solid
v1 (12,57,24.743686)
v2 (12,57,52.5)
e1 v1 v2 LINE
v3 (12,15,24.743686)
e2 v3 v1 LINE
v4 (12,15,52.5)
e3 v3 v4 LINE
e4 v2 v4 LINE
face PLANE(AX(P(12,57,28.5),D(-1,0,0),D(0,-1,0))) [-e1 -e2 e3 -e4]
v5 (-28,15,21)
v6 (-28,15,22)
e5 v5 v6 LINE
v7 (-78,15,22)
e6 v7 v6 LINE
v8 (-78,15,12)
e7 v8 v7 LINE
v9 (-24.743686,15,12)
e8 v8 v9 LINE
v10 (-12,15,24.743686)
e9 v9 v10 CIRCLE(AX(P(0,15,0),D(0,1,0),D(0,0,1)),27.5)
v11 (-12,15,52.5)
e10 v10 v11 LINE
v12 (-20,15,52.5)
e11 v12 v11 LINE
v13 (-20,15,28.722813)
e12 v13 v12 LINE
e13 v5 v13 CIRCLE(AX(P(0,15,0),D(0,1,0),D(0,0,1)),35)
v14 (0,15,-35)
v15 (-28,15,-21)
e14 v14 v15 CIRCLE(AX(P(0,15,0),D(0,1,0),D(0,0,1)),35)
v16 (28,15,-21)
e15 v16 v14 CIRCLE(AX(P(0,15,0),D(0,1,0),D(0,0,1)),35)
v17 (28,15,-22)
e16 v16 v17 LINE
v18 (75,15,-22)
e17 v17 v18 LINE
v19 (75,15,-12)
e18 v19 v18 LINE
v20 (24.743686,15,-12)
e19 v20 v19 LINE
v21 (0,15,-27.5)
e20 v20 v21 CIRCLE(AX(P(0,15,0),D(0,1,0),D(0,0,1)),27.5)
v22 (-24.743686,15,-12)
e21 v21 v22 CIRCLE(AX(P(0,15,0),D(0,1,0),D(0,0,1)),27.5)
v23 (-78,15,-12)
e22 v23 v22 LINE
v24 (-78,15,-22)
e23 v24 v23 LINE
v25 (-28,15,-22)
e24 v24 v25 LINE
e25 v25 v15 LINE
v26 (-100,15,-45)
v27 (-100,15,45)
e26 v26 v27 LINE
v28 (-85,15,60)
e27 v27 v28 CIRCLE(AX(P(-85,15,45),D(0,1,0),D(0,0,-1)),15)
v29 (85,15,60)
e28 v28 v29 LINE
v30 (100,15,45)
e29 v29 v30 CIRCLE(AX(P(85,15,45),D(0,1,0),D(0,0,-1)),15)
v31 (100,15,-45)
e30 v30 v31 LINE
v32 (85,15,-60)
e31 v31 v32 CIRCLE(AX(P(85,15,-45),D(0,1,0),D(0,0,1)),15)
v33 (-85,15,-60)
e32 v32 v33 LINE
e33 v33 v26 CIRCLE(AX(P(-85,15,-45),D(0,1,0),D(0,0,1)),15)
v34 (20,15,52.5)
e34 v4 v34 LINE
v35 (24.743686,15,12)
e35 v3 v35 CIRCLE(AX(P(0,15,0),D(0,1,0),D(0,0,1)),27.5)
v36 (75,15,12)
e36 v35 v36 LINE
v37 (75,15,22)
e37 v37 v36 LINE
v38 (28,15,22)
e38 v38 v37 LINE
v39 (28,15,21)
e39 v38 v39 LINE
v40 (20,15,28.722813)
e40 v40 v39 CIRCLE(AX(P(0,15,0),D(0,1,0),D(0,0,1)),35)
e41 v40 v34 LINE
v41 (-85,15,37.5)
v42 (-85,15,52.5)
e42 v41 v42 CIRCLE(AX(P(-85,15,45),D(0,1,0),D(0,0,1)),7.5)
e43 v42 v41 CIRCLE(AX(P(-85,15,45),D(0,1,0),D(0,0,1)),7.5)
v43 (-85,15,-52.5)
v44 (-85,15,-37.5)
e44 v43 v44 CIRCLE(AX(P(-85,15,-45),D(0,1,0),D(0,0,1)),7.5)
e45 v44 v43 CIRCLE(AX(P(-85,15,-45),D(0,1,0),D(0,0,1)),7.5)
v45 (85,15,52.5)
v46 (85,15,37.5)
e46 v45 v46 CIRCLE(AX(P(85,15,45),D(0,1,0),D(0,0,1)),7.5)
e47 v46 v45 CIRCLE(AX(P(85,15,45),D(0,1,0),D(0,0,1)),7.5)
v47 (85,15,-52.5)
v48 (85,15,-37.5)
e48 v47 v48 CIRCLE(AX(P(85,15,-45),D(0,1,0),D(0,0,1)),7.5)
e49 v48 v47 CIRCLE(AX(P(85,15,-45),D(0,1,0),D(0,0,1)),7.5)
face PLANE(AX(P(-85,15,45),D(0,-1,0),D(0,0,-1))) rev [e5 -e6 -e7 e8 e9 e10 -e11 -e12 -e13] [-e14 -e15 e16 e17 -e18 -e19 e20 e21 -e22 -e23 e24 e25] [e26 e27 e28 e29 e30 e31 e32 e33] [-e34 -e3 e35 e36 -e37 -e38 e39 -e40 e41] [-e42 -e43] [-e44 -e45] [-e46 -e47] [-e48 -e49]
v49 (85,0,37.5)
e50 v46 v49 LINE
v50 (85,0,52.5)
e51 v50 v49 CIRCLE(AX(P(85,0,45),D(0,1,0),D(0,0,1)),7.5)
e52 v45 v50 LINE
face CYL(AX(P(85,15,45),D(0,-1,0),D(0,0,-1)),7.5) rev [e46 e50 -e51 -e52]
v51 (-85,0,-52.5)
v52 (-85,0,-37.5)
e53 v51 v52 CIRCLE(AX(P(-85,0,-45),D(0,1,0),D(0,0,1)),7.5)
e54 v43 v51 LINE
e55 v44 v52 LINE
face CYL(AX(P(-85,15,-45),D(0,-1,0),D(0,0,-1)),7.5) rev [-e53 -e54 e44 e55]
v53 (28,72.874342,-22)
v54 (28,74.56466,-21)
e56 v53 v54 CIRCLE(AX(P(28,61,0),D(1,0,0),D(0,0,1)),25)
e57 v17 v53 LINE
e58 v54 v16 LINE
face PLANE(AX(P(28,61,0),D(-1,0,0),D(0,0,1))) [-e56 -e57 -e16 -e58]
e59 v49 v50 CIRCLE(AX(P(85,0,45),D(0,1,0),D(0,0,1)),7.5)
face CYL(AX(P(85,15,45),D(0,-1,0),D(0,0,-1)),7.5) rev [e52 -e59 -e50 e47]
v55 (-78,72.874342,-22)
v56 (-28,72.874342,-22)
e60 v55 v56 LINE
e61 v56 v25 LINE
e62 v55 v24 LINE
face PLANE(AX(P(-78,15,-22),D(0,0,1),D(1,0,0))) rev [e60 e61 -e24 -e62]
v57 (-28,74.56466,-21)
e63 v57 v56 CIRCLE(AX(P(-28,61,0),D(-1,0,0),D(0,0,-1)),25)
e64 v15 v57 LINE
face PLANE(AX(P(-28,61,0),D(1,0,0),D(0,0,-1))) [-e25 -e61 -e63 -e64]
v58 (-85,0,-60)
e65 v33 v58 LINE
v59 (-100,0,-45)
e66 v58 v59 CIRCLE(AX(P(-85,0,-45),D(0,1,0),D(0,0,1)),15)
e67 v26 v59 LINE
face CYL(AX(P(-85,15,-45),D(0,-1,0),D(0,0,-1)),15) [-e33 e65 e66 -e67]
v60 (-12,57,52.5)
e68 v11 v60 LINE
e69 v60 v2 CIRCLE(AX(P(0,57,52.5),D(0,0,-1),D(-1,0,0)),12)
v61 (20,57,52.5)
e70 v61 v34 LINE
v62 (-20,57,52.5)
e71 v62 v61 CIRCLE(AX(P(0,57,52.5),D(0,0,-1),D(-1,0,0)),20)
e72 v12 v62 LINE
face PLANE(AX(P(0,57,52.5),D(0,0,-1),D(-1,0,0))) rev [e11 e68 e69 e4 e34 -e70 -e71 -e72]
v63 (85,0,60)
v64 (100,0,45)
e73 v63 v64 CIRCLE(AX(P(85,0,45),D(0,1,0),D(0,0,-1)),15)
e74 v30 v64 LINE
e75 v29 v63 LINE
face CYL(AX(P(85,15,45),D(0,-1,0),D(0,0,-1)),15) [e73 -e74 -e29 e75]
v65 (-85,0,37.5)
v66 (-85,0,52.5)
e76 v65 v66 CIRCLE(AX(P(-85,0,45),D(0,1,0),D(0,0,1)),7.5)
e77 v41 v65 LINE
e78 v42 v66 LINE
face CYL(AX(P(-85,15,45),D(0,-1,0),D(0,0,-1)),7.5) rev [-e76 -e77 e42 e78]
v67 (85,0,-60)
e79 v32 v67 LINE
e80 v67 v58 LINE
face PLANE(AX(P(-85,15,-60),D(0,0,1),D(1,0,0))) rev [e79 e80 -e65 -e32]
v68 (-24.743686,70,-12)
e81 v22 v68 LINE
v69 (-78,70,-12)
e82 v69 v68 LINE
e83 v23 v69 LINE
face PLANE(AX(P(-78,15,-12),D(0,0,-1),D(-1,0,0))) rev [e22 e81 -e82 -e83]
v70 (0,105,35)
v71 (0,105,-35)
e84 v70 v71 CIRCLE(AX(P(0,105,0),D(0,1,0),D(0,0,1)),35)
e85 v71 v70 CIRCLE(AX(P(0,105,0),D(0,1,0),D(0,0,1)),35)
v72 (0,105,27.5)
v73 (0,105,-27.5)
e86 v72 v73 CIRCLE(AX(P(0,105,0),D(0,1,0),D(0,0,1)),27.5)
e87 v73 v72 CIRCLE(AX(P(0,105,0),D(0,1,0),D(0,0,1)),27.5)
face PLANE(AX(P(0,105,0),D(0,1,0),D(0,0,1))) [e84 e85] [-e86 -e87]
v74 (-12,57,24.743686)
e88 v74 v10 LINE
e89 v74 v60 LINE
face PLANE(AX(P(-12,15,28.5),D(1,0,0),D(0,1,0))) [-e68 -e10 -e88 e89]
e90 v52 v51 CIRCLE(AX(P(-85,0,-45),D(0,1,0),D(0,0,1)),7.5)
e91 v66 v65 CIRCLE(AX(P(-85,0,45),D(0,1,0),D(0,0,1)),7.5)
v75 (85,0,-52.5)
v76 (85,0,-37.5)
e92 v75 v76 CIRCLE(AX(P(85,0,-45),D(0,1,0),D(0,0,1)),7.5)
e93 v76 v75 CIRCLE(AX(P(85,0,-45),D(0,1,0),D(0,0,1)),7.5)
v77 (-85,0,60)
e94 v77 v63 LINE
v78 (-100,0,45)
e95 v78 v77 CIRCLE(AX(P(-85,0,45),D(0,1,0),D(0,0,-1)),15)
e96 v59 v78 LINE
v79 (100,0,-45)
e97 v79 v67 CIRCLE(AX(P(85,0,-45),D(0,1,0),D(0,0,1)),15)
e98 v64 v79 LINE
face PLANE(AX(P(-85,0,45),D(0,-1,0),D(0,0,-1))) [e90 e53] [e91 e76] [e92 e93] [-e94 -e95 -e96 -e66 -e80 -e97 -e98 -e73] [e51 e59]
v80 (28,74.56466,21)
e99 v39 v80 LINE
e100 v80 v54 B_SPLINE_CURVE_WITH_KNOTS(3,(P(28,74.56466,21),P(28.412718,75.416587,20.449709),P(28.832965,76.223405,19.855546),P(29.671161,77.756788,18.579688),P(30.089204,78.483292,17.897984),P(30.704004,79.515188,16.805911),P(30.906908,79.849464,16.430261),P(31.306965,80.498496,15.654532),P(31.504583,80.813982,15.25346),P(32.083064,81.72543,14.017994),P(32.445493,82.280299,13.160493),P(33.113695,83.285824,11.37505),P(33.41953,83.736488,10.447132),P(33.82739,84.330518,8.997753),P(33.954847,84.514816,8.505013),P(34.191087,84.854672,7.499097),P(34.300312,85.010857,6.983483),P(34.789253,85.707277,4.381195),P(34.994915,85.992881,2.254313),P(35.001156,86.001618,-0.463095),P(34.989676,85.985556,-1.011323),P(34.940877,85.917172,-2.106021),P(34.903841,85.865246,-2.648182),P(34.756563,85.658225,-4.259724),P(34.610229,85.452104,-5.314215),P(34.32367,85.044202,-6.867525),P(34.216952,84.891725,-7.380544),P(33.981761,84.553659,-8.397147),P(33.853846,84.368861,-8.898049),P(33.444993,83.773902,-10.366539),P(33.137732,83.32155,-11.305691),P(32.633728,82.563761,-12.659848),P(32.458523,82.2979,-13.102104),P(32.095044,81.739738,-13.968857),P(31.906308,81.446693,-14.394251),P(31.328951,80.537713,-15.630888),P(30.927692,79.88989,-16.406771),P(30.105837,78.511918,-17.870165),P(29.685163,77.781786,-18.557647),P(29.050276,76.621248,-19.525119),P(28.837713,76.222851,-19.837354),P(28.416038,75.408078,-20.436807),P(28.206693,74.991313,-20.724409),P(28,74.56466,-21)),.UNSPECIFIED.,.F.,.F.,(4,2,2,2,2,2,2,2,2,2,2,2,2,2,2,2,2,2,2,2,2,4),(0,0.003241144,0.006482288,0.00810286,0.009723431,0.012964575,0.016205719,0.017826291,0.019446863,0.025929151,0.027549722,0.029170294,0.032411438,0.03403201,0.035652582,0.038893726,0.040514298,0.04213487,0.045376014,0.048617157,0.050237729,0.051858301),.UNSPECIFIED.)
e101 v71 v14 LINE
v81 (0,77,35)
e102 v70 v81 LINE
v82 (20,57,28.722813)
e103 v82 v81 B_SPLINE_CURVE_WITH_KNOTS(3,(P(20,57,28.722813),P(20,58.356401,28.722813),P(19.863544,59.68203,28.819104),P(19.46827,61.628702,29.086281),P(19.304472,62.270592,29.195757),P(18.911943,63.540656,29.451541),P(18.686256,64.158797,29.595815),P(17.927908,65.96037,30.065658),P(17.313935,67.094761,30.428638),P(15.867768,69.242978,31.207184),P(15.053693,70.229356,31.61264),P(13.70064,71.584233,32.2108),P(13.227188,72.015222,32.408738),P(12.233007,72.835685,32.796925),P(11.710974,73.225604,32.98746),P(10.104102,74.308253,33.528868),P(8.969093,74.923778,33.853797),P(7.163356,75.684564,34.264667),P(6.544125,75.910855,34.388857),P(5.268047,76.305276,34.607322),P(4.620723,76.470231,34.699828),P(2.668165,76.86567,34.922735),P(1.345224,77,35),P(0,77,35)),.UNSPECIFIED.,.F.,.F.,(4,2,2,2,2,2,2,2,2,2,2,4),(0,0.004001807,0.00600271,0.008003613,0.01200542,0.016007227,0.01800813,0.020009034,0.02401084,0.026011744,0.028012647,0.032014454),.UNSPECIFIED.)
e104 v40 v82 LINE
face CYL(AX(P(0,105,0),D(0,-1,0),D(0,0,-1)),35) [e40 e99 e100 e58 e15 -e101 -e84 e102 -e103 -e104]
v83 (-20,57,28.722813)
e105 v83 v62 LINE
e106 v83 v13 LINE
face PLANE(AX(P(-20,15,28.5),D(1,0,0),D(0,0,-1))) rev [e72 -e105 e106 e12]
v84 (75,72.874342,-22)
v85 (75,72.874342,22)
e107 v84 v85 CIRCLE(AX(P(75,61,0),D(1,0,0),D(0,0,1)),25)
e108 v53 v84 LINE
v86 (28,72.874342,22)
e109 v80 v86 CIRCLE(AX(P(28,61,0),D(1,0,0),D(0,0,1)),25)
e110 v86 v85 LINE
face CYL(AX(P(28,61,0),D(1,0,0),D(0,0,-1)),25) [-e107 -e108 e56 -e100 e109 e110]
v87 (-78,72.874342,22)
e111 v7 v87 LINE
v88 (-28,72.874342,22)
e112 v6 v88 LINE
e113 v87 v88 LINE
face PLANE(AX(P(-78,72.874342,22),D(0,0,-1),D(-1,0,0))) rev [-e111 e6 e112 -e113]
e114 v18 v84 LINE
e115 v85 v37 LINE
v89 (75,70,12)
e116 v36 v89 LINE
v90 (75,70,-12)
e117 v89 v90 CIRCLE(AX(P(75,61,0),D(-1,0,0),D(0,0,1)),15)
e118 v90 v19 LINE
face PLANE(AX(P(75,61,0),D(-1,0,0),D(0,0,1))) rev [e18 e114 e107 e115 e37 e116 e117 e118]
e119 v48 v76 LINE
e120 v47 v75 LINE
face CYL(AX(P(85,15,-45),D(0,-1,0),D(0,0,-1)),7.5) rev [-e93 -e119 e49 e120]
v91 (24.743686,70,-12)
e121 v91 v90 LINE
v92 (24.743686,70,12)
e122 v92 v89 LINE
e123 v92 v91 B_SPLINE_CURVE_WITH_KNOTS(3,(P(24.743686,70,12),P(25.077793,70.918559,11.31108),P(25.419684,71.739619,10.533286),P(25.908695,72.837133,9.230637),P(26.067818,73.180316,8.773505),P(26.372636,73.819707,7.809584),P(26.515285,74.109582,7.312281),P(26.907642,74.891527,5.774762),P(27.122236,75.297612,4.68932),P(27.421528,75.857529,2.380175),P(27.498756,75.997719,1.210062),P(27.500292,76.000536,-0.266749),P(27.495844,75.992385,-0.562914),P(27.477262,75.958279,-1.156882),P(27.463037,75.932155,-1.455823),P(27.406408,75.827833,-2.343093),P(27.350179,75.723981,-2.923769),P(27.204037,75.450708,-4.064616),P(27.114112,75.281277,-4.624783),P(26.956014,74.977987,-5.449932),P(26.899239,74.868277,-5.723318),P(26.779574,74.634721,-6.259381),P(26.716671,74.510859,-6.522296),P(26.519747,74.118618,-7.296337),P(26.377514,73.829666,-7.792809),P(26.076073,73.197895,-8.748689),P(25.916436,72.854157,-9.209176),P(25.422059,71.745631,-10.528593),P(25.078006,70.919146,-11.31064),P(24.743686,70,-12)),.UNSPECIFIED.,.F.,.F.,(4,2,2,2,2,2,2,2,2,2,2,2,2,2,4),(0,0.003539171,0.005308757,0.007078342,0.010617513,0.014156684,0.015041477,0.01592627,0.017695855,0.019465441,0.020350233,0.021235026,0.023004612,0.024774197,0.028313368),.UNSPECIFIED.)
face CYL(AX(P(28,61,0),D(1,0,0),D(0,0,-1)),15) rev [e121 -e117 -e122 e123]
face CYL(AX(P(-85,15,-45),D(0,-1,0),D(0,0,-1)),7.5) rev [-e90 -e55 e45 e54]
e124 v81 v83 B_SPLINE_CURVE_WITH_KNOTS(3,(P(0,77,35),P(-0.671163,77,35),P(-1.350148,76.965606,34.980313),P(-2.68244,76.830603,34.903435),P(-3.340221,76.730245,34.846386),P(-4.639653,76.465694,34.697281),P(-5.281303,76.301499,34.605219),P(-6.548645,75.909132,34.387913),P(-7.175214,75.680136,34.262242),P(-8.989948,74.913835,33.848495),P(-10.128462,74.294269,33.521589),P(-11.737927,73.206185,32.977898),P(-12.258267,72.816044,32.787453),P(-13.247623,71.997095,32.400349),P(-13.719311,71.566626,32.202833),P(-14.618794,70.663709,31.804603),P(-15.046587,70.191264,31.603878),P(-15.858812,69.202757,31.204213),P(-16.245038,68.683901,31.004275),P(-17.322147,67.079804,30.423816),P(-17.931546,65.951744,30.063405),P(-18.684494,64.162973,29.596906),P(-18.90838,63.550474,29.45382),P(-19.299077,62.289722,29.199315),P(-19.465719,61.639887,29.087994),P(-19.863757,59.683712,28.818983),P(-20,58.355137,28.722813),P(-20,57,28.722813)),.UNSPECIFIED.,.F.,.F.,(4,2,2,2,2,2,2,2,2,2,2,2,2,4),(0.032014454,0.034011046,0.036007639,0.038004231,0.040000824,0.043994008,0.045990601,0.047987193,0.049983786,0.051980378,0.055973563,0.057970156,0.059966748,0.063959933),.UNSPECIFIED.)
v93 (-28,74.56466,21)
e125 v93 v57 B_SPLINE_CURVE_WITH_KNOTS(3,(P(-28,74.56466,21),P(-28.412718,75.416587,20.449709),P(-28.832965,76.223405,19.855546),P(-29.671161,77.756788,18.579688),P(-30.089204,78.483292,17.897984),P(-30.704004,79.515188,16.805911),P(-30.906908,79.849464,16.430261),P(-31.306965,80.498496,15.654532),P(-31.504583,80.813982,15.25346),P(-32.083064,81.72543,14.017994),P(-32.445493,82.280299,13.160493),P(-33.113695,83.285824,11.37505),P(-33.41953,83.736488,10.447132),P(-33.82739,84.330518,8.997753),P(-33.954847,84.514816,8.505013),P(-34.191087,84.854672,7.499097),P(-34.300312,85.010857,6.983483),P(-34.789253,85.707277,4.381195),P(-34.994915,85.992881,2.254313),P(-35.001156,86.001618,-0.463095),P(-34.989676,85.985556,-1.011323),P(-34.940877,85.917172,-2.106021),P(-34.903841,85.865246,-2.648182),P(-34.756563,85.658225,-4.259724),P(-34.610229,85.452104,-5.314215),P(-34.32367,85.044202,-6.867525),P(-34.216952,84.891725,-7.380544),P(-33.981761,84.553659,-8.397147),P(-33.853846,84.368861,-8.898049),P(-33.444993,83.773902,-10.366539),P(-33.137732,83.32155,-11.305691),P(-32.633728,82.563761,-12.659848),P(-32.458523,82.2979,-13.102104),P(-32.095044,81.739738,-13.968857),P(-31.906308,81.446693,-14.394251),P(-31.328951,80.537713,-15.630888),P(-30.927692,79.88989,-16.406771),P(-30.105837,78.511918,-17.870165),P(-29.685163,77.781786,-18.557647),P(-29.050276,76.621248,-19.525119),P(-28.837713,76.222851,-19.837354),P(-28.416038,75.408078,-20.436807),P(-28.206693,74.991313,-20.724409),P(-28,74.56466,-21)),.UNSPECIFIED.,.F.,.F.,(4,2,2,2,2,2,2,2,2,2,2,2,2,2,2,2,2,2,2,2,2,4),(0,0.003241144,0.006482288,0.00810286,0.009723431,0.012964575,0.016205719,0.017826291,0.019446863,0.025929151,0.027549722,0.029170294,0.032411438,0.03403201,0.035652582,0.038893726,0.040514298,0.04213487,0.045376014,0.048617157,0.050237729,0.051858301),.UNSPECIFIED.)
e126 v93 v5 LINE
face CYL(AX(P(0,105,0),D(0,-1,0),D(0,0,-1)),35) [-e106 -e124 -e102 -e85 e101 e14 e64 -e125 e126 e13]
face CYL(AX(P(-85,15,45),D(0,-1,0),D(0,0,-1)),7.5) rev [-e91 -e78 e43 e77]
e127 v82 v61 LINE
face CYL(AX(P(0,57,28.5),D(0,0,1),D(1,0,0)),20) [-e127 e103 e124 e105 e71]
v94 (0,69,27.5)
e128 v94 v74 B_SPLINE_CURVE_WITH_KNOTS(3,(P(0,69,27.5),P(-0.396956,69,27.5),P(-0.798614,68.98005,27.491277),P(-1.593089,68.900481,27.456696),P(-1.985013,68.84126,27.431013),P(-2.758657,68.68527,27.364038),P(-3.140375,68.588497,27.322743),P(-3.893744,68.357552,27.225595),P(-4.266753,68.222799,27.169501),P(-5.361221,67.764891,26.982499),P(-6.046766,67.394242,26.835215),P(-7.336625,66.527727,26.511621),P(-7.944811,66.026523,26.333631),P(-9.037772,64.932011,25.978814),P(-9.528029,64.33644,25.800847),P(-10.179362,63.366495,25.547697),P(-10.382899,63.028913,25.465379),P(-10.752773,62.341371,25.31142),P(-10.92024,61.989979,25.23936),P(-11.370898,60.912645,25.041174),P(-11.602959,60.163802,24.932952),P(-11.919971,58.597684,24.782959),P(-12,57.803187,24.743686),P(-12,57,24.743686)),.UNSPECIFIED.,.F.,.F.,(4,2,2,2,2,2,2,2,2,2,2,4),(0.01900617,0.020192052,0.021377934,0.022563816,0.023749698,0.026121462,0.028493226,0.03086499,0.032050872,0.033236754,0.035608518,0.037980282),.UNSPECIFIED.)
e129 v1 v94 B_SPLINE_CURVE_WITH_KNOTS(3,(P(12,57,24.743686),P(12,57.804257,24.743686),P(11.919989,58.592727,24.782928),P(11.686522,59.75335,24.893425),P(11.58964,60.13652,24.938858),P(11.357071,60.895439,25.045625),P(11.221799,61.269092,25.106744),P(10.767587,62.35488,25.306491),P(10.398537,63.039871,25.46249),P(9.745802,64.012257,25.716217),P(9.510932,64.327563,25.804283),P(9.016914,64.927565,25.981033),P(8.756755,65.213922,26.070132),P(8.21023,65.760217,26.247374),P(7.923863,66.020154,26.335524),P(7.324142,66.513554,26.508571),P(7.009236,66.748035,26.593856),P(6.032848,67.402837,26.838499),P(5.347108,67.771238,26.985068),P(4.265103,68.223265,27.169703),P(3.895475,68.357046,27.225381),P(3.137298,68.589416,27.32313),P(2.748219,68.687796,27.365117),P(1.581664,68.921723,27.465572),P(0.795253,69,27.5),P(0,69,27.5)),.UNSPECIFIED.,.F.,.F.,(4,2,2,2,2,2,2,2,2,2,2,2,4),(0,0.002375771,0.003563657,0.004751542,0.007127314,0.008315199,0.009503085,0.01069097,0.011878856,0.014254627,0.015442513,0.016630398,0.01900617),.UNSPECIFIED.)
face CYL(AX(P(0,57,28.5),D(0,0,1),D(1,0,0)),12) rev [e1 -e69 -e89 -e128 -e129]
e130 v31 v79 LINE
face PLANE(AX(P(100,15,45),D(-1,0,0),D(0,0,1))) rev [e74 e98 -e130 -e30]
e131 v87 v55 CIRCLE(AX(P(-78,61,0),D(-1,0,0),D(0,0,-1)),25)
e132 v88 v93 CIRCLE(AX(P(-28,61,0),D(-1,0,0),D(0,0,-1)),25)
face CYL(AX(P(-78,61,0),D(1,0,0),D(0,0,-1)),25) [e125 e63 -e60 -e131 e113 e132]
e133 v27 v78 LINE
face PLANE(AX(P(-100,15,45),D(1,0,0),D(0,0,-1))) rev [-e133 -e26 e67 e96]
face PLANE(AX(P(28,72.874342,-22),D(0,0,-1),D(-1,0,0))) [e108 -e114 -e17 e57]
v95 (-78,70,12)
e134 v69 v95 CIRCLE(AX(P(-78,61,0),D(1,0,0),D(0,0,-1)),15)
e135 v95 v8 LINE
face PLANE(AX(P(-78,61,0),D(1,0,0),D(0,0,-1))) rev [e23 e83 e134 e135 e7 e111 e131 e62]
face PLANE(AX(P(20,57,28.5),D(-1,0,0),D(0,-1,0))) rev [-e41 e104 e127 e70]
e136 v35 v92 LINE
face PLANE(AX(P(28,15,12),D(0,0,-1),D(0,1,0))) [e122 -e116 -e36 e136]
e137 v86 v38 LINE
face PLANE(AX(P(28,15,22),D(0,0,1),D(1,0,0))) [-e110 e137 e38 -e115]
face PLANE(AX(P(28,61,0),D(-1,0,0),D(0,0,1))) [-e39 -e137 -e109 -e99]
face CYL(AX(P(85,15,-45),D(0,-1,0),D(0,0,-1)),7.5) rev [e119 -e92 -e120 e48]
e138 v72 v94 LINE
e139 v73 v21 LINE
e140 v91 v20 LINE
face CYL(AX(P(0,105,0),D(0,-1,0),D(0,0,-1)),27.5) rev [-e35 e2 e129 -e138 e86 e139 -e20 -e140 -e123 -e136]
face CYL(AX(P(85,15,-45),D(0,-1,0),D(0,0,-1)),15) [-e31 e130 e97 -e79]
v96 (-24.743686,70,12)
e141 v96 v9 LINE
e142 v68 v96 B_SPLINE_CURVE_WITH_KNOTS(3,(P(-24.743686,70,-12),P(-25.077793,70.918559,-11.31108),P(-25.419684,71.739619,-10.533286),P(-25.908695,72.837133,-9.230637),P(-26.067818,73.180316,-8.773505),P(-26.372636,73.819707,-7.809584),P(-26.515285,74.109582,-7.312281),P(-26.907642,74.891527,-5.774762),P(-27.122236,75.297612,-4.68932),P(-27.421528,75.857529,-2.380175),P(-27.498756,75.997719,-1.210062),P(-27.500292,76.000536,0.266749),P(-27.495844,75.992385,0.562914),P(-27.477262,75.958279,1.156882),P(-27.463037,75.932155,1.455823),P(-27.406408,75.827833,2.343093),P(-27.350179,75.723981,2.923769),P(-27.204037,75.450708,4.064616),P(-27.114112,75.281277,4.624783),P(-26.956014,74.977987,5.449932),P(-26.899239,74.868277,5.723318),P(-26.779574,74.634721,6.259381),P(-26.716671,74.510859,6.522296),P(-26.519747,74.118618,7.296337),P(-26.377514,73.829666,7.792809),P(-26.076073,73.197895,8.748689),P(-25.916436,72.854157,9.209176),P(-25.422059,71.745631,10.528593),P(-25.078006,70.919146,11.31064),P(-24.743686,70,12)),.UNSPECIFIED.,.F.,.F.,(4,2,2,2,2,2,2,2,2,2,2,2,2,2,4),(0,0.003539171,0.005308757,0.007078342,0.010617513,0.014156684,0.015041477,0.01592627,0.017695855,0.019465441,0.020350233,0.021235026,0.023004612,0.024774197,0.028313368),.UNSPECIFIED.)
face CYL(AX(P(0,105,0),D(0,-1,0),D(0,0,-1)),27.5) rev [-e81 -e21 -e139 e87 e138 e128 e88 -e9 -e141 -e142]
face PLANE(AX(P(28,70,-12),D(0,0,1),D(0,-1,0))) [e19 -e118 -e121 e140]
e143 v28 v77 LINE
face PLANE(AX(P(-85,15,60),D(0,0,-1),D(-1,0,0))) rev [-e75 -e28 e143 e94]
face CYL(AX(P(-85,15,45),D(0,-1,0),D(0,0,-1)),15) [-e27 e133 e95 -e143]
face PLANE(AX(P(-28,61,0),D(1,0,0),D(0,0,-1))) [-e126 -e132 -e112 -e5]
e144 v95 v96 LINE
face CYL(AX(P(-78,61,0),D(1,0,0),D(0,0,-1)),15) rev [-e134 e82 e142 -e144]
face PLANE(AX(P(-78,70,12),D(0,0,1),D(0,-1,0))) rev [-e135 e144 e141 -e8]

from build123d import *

# Parameters (mm, degrees)
BASE_PLATE_SKETCH_R         = 7.5
BASE_PLATE_200X120X15_DEPTH = 15
TUBE_BOSS_SKETCH_R          = 35
TUBE_BOSS_SKETCH_R_2        = 27.5
TUBE_BOSS_55_BORE_35_DEPTH  = 90
FRONT_LUG_DEPTH             = 24
FRONT_LUG_CUT_DEPTH         = 40
SIDE_LUG_A_DEPTH            = 3
SIDE_LUG_A_DEPTH_BACK       = 47
SIDE_START                  = -73
SIDE_LUG_A_SLOT_DEPTH       = 73
SIDE_LUG_B_DEPTH            = 47
SIDE_LUG_B_SLOT_DEPTH       = 67


with BuildPart() as part:
    # Base Plate Sketch → Base Plate 200x120x15 (new body)
    with BuildSketch(Plane(origin=(0, 0, 0), x_dir=(1, 0, 0), z_dir=(0, 1, 0))):
        with BuildLine():
            Line((-85, -60), (85, -60))
            ThreePointArc((85, -60), (95.606601718, -55.606601718), (100, -45))
            Line((100, -45), (100, 45))
            ThreePointArc((100, 45), (95.606601718, 55.606601718), (85, 60))
            Line((85, 60), (-85, 60))
            ThreePointArc((-85, 60), (-95.606601718, 55.606601718), (-100, 45))
            Line((-100, 45), (-100, -45))
            ThreePointArc((-100, -45), (-95.606601718, -55.606601718), (-85, -60))
        make_face()
        with Locations(Location((-85, 45, 0), (0, 0, 270))):
            Circle(BASE_PLATE_SKETCH_R, mode=Mode.SUBTRACT)
        with Locations(Location((85, 45, 0), (0, 0, 270))):
            Circle(BASE_PLATE_SKETCH_R, mode=Mode.SUBTRACT)
        with Locations(Location((85, -45, 0), (0, 0, 270))):
            Circle(BASE_PLATE_SKETCH_R, mode=Mode.SUBTRACT)
        with Locations(Location((-85, -45, 0), (0, 0, 270))):
            Circle(BASE_PLATE_SKETCH_R, mode=Mode.SUBTRACT)
    extrude(amount=BASE_PLATE_200X120X15_DEPTH)

    # Tube Boss Sketch → Tube Boss Ø55 Bore Ø35 (add)
    with BuildSketch(Plane(origin=(0, 15, 0), x_dir=(1, 0, 0), z_dir=(0, 1, 0))):
        with Locations(Location((0, 0, 0), (0, 0, 90))):
            Circle(TUBE_BOSS_SKETCH_R)
        with Locations(Location((0, 0, 0), (0, 0, 90))):
            Circle(TUBE_BOSS_SKETCH_R_2, mode=Mode.SUBTRACT)
    extrude(amount=TUBE_BOSS_55_BORE_35_DEPTH)

    # Front Lug Sketch → Front Lug (add)
    with BuildSketch(Plane.XY.offset(52.5)):
        with BuildLine():
            Line((-12, 15), (-12, 57))
            ThreePointArc((-12, 57), (0, 69), (12, 57))
            Line((12, 57), (12, 15))
            Line((12, 15), (20, 15))
            Line((20, 15), (20, 57))
            ThreePointArc((20, 57), (0, 77), (-20, 57))
            Line((-20, 57), (-20, 15))
            Line((-20, 15), (-12, 15))
        make_face()
    extrude(amount=-FRONT_LUG_DEPTH)

    # Front Lug Cut Sketch → Front Lug Cut (cut)
    with BuildSketch(Plane.XY.offset(52.5)):
        with BuildLine():
            Line((-12, 15), (12, 15))
            Line((12, 15), (12, 57))
            ThreePointArc((12, 57), (0, 69), (-12, 57))
            Line((-12, 57), (-12, 15))
        make_face()
    extrude(amount=-FRONT_LUG_CUT_DEPTH, mode=Mode.SUBTRACT)

    # Side Lug A Sketch → Side Lug A (add, two sides: drawn at the far end of the back side and taken through both)
    with BuildSketch(Plane.ZY.offset(75).offset(-SIDE_LUG_A_DEPTH_BACK)):
        with BuildLine():
            Line((-12, 15), (-12, 70))
            ThreePointArc((-12, 70), (0, 76), (12, 70))
            Line((12, 70), (12, 15))
            Line((12, 15), (22, 15))
            Line((22, 15), (22, 72.874342087))
            ThreePointArc((22, 72.874342087), (0, 86), (-22, 72.874342087))
            Line((-22, 72.874342087), (-22, 15))
            Line((-22, 15), (-12, 15))
        make_face()
    extrude(amount=SIDE_LUG_A_DEPTH + SIDE_LUG_A_DEPTH_BACK)

    # Side Lug A Slot Sketch → Side Lug A Slot (cut)
    with BuildSketch(Plane.ZY.offset(78).offset(SIDE_START)):
        with BuildLine():
            Line((12, 70), (12, 15))
            Line((12, 15), (-12, 15))
            Line((-12, 15), (-12, 70))
            ThreePointArc((-12, 70), (0, 76), (12, 70))
        make_face()
    extrude(amount=SIDE_LUG_A_SLOT_DEPTH, mode=Mode.SUBTRACT)

    # Side Lug B Sketch → Side Lug B (add)
    with BuildSketch(Plane(origin=(75, 0, 0), x_dir=(0, 0, -1), z_dir=(1, 0, 0))):
        with BuildLine():
            Line((-12, 15), (-12, 70))
            ThreePointArc((-12, 70), (0, 76), (12, 70))
            Line((12, 70), (12, 15))
            Line((12, 15), (22, 15))
            Line((22, 15), (22, 72.874342087))
            ThreePointArc((22, 72.874342087), (0, 86), (-22, 72.874342087))
            Line((-22, 72.874342087), (-22, 15))
            Line((-22, 15), (-12, 15))
        make_face()
    extrude(amount=-SIDE_LUG_B_DEPTH)

    # Side Lug B Slot Sketch → Side Lug B Slot (cut)
    with BuildSketch(Plane(origin=(75, 0, 0), x_dir=(0, 0, -1), z_dir=(1, 0, 0))):
        with BuildLine():
            Line((12, 15), (12, 70))
            ThreePointArc((12, 70), (0, 76), (-12, 70))
            Line((-12, 70), (-12, 15))
            Line((-12, 15), (12, 15))
        make_face()
    extrude(amount=-SIDE_LUG_B_SLOT_DEPTH, mode=Mode.SUBTRACT)


solid = part.part
